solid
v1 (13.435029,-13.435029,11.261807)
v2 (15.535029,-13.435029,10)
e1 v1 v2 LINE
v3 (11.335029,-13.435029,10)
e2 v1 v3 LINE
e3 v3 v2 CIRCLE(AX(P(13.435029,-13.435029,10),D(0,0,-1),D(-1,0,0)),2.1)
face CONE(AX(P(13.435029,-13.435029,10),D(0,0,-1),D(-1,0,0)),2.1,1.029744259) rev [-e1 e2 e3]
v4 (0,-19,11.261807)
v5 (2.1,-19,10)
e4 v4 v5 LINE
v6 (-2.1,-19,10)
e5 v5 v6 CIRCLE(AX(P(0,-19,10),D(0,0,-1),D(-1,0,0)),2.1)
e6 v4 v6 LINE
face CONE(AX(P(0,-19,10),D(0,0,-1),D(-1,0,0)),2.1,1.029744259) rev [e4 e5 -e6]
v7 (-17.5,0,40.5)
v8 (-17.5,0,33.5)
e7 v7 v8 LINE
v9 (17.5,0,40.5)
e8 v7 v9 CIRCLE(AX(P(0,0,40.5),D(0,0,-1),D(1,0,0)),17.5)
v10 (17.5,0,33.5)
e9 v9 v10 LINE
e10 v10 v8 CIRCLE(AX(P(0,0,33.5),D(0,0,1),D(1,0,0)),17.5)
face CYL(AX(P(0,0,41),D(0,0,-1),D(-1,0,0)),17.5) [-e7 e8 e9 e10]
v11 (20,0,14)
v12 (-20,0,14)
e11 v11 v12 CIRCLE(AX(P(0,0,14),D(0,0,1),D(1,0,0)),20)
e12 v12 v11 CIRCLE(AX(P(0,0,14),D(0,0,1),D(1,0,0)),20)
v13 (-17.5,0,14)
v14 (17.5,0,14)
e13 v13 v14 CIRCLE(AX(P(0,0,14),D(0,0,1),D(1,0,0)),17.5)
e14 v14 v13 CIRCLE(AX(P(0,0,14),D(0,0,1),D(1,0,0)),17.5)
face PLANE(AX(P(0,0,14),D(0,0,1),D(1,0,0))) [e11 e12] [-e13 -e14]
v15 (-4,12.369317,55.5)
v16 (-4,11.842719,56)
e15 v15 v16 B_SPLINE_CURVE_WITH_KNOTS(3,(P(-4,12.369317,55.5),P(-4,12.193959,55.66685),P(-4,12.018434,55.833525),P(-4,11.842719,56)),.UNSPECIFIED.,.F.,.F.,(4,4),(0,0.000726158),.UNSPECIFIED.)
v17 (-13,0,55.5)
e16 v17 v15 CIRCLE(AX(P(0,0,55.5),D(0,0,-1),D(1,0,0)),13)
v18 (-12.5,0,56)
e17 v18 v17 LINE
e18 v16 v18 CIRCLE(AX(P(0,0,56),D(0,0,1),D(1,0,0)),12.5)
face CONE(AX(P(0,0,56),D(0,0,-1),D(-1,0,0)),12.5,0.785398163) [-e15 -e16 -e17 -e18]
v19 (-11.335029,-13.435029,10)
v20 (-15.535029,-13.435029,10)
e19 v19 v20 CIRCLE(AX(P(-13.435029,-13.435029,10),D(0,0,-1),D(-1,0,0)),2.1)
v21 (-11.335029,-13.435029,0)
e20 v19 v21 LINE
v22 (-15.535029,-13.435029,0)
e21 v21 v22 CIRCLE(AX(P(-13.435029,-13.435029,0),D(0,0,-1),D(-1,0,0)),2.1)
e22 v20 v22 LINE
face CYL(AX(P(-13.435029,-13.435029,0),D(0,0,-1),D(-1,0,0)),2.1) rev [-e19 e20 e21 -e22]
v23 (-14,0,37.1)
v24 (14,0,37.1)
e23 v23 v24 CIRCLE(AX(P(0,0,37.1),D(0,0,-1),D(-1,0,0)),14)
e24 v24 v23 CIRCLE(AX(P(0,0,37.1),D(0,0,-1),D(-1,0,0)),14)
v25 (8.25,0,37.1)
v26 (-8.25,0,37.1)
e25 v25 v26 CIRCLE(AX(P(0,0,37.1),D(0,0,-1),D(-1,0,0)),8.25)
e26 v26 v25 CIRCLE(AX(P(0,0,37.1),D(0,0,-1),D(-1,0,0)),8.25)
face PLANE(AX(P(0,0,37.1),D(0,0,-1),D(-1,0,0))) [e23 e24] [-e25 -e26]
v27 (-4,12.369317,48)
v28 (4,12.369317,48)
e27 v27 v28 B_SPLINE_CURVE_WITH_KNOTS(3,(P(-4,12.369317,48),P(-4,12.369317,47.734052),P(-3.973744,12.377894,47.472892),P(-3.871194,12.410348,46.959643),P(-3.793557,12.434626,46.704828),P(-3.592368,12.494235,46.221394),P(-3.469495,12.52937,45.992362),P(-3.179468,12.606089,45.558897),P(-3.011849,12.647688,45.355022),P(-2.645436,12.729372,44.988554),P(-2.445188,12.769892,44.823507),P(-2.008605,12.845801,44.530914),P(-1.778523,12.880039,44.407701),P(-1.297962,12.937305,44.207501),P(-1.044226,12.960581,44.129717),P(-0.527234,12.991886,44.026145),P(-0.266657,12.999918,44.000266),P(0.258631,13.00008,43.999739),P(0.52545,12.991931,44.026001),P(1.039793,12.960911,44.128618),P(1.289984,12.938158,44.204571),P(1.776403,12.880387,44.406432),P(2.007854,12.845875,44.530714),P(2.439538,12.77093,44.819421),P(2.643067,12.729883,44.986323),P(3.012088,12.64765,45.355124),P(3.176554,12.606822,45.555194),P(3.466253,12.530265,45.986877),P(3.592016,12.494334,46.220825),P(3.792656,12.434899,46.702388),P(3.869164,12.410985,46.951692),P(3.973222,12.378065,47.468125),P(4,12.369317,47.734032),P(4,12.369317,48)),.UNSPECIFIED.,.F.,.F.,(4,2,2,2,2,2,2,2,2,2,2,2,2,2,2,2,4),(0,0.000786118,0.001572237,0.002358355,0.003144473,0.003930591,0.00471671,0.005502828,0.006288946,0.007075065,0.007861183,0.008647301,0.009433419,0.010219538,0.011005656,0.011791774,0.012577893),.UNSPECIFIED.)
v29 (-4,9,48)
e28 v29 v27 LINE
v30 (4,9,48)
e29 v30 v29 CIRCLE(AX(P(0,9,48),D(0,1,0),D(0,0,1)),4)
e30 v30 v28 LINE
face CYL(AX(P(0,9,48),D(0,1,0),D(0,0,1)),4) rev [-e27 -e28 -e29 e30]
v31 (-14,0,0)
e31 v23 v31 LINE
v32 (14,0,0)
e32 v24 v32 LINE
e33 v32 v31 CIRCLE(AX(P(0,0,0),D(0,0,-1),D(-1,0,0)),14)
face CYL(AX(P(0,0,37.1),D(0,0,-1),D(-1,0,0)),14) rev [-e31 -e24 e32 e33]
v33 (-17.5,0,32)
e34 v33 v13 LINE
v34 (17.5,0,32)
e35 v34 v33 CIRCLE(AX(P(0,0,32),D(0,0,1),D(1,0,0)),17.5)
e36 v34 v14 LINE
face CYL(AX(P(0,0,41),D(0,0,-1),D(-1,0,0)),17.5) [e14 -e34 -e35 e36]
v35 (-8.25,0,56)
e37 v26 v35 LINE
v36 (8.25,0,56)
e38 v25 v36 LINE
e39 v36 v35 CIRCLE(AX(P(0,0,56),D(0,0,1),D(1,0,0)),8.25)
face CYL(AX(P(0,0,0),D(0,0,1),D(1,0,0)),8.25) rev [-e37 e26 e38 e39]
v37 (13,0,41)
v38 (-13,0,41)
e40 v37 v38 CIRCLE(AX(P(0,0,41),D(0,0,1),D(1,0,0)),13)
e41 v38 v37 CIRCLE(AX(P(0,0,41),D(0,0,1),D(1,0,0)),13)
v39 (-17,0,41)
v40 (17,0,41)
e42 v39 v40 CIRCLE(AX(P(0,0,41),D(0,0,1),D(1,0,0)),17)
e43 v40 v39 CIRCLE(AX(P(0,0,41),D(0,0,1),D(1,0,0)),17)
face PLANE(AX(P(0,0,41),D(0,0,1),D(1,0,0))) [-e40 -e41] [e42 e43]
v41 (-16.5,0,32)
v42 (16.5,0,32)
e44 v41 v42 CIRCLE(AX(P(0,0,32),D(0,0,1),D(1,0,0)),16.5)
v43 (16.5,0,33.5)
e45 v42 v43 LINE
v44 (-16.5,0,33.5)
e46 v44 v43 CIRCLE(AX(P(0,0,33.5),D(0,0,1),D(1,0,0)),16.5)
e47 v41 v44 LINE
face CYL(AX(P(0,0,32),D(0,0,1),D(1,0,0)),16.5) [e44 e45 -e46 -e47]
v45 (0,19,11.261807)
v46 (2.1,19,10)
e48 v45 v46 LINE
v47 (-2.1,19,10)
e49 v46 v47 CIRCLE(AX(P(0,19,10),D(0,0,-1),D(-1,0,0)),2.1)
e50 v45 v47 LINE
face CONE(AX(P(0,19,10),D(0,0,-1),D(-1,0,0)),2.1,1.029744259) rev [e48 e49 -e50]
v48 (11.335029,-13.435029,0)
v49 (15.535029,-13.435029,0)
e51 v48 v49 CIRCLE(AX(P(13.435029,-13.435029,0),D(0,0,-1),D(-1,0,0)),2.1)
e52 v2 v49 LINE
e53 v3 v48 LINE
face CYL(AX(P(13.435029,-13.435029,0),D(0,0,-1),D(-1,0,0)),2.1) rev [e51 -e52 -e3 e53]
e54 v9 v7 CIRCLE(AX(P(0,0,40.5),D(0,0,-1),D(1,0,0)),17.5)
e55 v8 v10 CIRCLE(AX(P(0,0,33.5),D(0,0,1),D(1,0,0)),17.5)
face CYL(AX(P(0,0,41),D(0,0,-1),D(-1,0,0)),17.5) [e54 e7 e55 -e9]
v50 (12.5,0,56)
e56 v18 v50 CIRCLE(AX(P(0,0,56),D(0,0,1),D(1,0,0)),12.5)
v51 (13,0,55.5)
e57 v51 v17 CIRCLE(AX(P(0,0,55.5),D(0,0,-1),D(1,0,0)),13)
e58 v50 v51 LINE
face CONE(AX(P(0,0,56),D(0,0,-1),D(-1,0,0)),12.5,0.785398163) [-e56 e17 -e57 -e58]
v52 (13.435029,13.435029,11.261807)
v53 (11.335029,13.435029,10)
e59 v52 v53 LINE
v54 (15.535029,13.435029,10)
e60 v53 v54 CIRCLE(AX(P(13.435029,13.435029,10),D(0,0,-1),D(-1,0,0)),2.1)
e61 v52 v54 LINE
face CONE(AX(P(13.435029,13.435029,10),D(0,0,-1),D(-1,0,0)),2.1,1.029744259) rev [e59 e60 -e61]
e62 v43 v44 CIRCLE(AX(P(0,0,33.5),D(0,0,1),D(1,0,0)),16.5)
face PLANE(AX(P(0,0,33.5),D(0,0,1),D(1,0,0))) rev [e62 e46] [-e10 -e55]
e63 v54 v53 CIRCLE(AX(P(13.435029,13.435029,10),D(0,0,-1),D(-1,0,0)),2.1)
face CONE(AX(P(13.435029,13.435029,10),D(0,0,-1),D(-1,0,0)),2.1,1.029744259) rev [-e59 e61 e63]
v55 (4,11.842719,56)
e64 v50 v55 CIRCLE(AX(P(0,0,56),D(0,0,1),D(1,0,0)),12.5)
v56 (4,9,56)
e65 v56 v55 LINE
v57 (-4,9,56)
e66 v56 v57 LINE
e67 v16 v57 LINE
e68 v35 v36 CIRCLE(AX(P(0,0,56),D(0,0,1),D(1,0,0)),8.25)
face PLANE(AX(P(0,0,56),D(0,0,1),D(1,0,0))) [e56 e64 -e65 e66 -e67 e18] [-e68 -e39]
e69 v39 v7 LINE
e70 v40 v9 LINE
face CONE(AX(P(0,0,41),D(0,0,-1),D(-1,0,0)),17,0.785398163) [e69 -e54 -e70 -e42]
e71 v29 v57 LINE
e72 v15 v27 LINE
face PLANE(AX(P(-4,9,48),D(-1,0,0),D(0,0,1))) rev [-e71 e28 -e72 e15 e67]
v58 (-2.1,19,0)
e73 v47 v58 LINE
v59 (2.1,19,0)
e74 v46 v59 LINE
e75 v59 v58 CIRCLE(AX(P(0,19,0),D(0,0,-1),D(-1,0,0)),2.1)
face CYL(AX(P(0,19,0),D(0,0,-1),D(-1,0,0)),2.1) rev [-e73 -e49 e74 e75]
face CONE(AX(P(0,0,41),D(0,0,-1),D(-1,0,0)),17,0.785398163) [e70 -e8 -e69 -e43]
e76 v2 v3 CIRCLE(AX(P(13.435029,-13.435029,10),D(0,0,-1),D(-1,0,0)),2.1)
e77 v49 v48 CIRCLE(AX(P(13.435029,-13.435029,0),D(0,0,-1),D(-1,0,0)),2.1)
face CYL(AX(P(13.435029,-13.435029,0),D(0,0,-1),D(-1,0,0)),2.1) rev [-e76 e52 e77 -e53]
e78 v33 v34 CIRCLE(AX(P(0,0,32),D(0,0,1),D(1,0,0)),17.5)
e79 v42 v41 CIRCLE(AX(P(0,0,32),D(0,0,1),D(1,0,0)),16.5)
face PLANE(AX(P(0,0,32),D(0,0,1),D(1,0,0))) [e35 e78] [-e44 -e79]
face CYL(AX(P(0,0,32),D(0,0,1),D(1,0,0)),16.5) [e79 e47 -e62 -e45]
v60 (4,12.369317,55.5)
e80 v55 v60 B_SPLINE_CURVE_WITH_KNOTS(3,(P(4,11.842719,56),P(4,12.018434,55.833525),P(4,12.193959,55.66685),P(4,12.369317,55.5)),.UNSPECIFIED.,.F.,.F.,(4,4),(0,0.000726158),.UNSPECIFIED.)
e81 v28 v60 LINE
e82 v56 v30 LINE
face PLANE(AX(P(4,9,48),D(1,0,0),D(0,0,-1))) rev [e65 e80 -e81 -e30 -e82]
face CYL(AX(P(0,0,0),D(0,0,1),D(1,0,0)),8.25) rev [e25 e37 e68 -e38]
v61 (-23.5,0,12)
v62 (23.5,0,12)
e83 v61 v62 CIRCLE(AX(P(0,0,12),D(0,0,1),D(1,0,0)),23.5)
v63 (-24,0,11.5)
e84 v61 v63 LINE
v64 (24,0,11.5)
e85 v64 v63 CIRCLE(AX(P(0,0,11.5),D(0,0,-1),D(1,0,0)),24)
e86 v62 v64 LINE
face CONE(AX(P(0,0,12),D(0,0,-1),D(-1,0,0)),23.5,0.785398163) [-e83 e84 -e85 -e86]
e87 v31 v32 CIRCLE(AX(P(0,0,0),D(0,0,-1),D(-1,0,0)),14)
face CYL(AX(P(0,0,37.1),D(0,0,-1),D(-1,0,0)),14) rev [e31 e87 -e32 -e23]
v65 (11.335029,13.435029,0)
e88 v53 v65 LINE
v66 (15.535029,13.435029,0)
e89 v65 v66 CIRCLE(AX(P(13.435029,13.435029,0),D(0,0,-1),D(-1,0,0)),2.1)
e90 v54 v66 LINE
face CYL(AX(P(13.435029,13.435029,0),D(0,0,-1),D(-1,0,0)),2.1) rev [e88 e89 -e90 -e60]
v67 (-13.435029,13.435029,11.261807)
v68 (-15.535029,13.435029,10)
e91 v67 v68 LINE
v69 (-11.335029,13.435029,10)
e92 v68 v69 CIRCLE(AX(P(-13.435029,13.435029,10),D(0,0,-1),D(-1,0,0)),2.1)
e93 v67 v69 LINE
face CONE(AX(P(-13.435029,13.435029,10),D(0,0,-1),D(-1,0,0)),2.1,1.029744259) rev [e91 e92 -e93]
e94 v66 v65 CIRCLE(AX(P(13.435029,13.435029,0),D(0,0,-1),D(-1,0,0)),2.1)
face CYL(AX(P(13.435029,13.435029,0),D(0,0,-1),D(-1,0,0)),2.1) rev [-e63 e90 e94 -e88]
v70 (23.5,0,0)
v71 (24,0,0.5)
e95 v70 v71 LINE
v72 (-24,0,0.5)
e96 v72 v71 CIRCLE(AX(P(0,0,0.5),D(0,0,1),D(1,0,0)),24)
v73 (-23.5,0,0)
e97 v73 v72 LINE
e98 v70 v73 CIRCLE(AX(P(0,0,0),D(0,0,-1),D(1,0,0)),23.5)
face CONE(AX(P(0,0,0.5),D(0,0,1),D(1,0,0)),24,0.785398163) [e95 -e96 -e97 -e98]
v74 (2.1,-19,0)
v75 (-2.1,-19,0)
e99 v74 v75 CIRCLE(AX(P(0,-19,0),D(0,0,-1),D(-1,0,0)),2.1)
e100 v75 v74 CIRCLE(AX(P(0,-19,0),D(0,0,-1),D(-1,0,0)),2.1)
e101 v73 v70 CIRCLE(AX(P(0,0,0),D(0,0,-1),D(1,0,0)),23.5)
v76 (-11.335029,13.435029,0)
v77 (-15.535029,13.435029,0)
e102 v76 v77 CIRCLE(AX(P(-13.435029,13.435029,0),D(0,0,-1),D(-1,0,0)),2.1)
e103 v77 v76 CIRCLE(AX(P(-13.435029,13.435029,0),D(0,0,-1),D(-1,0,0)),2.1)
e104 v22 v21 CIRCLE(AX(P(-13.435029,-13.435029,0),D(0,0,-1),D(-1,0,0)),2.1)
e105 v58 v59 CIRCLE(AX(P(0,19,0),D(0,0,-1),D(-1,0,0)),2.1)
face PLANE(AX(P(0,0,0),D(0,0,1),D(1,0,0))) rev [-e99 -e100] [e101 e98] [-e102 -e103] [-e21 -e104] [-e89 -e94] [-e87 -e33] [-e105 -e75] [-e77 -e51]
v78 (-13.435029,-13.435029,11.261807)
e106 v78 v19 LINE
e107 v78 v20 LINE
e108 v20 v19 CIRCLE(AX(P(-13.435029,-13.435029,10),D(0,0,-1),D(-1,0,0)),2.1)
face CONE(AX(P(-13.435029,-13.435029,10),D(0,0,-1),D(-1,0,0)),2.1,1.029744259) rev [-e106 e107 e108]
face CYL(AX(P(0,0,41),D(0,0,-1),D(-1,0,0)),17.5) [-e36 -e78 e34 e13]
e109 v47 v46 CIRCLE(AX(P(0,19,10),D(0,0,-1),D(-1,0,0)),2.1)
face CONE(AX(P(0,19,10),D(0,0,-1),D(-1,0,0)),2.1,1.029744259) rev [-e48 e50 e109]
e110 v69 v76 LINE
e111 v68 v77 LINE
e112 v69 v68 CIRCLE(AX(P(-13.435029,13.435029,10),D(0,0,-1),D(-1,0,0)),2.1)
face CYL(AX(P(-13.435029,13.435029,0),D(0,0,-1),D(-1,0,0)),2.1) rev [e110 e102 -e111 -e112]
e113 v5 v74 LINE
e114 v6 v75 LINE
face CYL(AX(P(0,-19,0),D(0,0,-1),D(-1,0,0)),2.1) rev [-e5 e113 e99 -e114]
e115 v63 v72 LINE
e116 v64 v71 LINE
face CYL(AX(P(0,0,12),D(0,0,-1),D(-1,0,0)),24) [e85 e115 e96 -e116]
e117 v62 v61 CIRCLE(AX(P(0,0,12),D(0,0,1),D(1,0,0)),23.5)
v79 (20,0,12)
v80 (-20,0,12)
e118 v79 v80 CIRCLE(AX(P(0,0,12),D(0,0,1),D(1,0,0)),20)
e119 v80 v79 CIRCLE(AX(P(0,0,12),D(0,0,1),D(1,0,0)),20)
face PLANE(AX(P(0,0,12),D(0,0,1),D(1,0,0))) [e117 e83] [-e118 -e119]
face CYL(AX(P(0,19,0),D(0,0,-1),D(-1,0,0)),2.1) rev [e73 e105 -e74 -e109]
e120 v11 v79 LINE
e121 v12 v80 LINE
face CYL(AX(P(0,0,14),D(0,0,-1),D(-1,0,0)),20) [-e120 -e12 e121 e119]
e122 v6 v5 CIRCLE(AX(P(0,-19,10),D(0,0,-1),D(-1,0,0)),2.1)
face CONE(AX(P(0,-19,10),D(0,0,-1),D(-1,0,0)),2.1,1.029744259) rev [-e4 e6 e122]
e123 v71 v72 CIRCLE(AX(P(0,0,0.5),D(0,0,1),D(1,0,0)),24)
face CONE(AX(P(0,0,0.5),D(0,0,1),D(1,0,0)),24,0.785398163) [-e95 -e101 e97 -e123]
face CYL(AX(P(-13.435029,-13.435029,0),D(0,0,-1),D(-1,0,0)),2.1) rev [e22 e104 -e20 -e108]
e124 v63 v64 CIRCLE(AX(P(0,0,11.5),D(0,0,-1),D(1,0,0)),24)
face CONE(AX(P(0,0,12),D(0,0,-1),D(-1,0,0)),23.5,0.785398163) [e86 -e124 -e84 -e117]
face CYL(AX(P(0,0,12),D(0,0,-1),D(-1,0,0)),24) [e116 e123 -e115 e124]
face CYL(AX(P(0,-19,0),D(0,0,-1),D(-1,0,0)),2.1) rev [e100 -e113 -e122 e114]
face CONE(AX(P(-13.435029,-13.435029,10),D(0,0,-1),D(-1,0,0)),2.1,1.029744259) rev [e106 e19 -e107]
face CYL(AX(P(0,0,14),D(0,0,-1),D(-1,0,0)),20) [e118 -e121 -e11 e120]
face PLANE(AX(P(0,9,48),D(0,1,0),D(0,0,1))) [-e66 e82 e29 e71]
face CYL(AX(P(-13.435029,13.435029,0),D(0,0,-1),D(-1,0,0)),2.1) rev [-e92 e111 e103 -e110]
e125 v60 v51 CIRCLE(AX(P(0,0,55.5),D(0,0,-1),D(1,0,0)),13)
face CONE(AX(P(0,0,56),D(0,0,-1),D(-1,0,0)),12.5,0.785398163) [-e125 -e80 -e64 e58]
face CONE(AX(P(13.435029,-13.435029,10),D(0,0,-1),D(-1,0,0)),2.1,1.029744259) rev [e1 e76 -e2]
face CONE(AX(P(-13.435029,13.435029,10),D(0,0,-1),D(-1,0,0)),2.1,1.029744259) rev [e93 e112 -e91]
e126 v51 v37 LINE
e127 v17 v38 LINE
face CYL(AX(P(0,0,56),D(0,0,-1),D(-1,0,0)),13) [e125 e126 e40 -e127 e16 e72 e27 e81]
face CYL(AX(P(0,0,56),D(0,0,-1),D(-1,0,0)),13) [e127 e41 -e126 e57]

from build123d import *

# Parameters (mm, degrees)
SKETCH1_R             = 24
BOSS_EXTRUDE1_DEPTH   = 12
SKETCH2_R             = 20
BOSS_EXTRUDE2_DEPTH   = 2
SKETCH3_R             = 17.5
BOSS_EXTRUDE3_DEPTH   = 27
SKETCH4_R             = 13
BOSS_EXTRUDE4_DEPTH   = 15
SKETCH5_R             = 14
CUT_EXTRUDE1_DEPTH    = 37.1
SKETCH6_R             = 8.25
CUT_EXTRUDE2_DEPTH    = 66.482822175
CUT_EXTRUDE3_DEPTH    = 4
CUT_EXTRUDE4_START    = -7.5
SKETCH8_R             = 29.21642444
SKETCH8_R_2           = 16.5
CUT_EXTRUDE4_DEPTH    = 1.5
M5_TAPPED_HOLE1_D     = 4.2
M5_TAPPED_HOLE1_DEPTH = 10
M5_TAPPED_HOLE1_TIP   = 1.2618073
CHAMFER1_SIZE         = 0.5


with BuildPart() as part:
    # Sketch1 → Boss-Extrude1 (new body)
    with BuildSketch(Plane.XY):
        Circle(SKETCH1_R)
    extrude(amount=BOSS_EXTRUDE1_DEPTH)

    # Sketch2 → Boss-Extrude2 (add)
    with BuildSketch(Plane.XY.offset(12)):
        Circle(SKETCH2_R)
    extrude(amount=BOSS_EXTRUDE2_DEPTH)

    # Sketch3 → Boss-Extrude3 (add)
    with BuildSketch(Plane.XY.offset(14)):
        Circle(SKETCH3_R)
    extrude(amount=BOSS_EXTRUDE3_DEPTH)

    # Sketch4 → Boss-Extrude4 (add)
    with BuildSketch(Plane.XY.offset(41)):
        Circle(SKETCH4_R)
    extrude(amount=BOSS_EXTRUDE4_DEPTH)

    # Sketch5 → Cut-Extrude1 (cut)
    with BuildSketch(Plane(origin=(0, 0, 0), x_dir=(-1, 0, 0), z_dir=(0, 0, -1))):
        Circle(SKETCH5_R)
    extrude(amount=-CUT_EXTRUDE1_DEPTH, mode=Mode.SUBTRACT)

    # Sketch6 → Cut-Extrude2 (cut, through all)
    with BuildSketch(Plane.XY.offset(56)):
        Circle(SKETCH6_R)
    extrude(amount=-CUT_EXTRUDE2_DEPTH, mode=Mode.SUBTRACT)

    # Sketch7 → Cut-Extrude3 (cut)
    with BuildSketch(Plane(origin=(0, 13, 0), x_dir=(1, 0, 0), z_dir=(0, 1, 0))):
        with BuildLine():
            Line((4, -48), (4, -64))
            ThreePointArc((4, -64), (0, -68), (-4, -64))
            Line((-4, -64), (-4, -48))
            ThreePointArc((-4, -48), (0, -44), (4, -48))
        make_face()
    extrude(amount=-CUT_EXTRUDE3_DEPTH, mode=Mode.SUBTRACT)

    # Sketch8 → Cut-Extrude4 (cut)
    with BuildSketch(Plane.XY.offset(41).offset(CUT_EXTRUDE4_START)):
        Circle(SKETCH8_R)
        Circle(SKETCH8_R_2, mode=Mode.SUBTRACT)
    extrude(amount=-CUT_EXTRUDE4_DEPTH, mode=Mode.SUBTRACT)

    # M5 Tapped Hole1
    with Locations(Plane(origin=(0, 0, 0), x_dir=(-1, 0, 0), z_dir=(0, 0, -1))):
        with Locations((0, 19), (-13.435028843, 13.435028843), (13.435028843, 13.435028843), (-13.435028843, -13.435028843), (0, -19), (13.435028843, -13.435028843)):
            Hole(M5_TAPPED_HOLE1_D / 2, depth=M5_TAPPED_HOLE1_DEPTH)
            with Locations((0, 0, -(M5_TAPPED_HOLE1_DEPTH + M5_TAPPED_HOLE1_TIP / 2))):  # 118° drill point
                Cone(0, M5_TAPPED_HOLE1_D / 2, M5_TAPPED_HOLE1_TIP, mode=Mode.SUBTRACT)

    # Chamfer1
    chamfer1_edges = [part.edges().sort_by_distance(p)[0] for p in [
        (-17.5, 0, 41),
        (-24, 0, 0),
        (-7.64852927, -10.511898021, 56),
        (-24, 0, 12),
    ]]
    chamfer(chamfer1_edges, length=CHAMFER1_SIZE)


solid = part.part
